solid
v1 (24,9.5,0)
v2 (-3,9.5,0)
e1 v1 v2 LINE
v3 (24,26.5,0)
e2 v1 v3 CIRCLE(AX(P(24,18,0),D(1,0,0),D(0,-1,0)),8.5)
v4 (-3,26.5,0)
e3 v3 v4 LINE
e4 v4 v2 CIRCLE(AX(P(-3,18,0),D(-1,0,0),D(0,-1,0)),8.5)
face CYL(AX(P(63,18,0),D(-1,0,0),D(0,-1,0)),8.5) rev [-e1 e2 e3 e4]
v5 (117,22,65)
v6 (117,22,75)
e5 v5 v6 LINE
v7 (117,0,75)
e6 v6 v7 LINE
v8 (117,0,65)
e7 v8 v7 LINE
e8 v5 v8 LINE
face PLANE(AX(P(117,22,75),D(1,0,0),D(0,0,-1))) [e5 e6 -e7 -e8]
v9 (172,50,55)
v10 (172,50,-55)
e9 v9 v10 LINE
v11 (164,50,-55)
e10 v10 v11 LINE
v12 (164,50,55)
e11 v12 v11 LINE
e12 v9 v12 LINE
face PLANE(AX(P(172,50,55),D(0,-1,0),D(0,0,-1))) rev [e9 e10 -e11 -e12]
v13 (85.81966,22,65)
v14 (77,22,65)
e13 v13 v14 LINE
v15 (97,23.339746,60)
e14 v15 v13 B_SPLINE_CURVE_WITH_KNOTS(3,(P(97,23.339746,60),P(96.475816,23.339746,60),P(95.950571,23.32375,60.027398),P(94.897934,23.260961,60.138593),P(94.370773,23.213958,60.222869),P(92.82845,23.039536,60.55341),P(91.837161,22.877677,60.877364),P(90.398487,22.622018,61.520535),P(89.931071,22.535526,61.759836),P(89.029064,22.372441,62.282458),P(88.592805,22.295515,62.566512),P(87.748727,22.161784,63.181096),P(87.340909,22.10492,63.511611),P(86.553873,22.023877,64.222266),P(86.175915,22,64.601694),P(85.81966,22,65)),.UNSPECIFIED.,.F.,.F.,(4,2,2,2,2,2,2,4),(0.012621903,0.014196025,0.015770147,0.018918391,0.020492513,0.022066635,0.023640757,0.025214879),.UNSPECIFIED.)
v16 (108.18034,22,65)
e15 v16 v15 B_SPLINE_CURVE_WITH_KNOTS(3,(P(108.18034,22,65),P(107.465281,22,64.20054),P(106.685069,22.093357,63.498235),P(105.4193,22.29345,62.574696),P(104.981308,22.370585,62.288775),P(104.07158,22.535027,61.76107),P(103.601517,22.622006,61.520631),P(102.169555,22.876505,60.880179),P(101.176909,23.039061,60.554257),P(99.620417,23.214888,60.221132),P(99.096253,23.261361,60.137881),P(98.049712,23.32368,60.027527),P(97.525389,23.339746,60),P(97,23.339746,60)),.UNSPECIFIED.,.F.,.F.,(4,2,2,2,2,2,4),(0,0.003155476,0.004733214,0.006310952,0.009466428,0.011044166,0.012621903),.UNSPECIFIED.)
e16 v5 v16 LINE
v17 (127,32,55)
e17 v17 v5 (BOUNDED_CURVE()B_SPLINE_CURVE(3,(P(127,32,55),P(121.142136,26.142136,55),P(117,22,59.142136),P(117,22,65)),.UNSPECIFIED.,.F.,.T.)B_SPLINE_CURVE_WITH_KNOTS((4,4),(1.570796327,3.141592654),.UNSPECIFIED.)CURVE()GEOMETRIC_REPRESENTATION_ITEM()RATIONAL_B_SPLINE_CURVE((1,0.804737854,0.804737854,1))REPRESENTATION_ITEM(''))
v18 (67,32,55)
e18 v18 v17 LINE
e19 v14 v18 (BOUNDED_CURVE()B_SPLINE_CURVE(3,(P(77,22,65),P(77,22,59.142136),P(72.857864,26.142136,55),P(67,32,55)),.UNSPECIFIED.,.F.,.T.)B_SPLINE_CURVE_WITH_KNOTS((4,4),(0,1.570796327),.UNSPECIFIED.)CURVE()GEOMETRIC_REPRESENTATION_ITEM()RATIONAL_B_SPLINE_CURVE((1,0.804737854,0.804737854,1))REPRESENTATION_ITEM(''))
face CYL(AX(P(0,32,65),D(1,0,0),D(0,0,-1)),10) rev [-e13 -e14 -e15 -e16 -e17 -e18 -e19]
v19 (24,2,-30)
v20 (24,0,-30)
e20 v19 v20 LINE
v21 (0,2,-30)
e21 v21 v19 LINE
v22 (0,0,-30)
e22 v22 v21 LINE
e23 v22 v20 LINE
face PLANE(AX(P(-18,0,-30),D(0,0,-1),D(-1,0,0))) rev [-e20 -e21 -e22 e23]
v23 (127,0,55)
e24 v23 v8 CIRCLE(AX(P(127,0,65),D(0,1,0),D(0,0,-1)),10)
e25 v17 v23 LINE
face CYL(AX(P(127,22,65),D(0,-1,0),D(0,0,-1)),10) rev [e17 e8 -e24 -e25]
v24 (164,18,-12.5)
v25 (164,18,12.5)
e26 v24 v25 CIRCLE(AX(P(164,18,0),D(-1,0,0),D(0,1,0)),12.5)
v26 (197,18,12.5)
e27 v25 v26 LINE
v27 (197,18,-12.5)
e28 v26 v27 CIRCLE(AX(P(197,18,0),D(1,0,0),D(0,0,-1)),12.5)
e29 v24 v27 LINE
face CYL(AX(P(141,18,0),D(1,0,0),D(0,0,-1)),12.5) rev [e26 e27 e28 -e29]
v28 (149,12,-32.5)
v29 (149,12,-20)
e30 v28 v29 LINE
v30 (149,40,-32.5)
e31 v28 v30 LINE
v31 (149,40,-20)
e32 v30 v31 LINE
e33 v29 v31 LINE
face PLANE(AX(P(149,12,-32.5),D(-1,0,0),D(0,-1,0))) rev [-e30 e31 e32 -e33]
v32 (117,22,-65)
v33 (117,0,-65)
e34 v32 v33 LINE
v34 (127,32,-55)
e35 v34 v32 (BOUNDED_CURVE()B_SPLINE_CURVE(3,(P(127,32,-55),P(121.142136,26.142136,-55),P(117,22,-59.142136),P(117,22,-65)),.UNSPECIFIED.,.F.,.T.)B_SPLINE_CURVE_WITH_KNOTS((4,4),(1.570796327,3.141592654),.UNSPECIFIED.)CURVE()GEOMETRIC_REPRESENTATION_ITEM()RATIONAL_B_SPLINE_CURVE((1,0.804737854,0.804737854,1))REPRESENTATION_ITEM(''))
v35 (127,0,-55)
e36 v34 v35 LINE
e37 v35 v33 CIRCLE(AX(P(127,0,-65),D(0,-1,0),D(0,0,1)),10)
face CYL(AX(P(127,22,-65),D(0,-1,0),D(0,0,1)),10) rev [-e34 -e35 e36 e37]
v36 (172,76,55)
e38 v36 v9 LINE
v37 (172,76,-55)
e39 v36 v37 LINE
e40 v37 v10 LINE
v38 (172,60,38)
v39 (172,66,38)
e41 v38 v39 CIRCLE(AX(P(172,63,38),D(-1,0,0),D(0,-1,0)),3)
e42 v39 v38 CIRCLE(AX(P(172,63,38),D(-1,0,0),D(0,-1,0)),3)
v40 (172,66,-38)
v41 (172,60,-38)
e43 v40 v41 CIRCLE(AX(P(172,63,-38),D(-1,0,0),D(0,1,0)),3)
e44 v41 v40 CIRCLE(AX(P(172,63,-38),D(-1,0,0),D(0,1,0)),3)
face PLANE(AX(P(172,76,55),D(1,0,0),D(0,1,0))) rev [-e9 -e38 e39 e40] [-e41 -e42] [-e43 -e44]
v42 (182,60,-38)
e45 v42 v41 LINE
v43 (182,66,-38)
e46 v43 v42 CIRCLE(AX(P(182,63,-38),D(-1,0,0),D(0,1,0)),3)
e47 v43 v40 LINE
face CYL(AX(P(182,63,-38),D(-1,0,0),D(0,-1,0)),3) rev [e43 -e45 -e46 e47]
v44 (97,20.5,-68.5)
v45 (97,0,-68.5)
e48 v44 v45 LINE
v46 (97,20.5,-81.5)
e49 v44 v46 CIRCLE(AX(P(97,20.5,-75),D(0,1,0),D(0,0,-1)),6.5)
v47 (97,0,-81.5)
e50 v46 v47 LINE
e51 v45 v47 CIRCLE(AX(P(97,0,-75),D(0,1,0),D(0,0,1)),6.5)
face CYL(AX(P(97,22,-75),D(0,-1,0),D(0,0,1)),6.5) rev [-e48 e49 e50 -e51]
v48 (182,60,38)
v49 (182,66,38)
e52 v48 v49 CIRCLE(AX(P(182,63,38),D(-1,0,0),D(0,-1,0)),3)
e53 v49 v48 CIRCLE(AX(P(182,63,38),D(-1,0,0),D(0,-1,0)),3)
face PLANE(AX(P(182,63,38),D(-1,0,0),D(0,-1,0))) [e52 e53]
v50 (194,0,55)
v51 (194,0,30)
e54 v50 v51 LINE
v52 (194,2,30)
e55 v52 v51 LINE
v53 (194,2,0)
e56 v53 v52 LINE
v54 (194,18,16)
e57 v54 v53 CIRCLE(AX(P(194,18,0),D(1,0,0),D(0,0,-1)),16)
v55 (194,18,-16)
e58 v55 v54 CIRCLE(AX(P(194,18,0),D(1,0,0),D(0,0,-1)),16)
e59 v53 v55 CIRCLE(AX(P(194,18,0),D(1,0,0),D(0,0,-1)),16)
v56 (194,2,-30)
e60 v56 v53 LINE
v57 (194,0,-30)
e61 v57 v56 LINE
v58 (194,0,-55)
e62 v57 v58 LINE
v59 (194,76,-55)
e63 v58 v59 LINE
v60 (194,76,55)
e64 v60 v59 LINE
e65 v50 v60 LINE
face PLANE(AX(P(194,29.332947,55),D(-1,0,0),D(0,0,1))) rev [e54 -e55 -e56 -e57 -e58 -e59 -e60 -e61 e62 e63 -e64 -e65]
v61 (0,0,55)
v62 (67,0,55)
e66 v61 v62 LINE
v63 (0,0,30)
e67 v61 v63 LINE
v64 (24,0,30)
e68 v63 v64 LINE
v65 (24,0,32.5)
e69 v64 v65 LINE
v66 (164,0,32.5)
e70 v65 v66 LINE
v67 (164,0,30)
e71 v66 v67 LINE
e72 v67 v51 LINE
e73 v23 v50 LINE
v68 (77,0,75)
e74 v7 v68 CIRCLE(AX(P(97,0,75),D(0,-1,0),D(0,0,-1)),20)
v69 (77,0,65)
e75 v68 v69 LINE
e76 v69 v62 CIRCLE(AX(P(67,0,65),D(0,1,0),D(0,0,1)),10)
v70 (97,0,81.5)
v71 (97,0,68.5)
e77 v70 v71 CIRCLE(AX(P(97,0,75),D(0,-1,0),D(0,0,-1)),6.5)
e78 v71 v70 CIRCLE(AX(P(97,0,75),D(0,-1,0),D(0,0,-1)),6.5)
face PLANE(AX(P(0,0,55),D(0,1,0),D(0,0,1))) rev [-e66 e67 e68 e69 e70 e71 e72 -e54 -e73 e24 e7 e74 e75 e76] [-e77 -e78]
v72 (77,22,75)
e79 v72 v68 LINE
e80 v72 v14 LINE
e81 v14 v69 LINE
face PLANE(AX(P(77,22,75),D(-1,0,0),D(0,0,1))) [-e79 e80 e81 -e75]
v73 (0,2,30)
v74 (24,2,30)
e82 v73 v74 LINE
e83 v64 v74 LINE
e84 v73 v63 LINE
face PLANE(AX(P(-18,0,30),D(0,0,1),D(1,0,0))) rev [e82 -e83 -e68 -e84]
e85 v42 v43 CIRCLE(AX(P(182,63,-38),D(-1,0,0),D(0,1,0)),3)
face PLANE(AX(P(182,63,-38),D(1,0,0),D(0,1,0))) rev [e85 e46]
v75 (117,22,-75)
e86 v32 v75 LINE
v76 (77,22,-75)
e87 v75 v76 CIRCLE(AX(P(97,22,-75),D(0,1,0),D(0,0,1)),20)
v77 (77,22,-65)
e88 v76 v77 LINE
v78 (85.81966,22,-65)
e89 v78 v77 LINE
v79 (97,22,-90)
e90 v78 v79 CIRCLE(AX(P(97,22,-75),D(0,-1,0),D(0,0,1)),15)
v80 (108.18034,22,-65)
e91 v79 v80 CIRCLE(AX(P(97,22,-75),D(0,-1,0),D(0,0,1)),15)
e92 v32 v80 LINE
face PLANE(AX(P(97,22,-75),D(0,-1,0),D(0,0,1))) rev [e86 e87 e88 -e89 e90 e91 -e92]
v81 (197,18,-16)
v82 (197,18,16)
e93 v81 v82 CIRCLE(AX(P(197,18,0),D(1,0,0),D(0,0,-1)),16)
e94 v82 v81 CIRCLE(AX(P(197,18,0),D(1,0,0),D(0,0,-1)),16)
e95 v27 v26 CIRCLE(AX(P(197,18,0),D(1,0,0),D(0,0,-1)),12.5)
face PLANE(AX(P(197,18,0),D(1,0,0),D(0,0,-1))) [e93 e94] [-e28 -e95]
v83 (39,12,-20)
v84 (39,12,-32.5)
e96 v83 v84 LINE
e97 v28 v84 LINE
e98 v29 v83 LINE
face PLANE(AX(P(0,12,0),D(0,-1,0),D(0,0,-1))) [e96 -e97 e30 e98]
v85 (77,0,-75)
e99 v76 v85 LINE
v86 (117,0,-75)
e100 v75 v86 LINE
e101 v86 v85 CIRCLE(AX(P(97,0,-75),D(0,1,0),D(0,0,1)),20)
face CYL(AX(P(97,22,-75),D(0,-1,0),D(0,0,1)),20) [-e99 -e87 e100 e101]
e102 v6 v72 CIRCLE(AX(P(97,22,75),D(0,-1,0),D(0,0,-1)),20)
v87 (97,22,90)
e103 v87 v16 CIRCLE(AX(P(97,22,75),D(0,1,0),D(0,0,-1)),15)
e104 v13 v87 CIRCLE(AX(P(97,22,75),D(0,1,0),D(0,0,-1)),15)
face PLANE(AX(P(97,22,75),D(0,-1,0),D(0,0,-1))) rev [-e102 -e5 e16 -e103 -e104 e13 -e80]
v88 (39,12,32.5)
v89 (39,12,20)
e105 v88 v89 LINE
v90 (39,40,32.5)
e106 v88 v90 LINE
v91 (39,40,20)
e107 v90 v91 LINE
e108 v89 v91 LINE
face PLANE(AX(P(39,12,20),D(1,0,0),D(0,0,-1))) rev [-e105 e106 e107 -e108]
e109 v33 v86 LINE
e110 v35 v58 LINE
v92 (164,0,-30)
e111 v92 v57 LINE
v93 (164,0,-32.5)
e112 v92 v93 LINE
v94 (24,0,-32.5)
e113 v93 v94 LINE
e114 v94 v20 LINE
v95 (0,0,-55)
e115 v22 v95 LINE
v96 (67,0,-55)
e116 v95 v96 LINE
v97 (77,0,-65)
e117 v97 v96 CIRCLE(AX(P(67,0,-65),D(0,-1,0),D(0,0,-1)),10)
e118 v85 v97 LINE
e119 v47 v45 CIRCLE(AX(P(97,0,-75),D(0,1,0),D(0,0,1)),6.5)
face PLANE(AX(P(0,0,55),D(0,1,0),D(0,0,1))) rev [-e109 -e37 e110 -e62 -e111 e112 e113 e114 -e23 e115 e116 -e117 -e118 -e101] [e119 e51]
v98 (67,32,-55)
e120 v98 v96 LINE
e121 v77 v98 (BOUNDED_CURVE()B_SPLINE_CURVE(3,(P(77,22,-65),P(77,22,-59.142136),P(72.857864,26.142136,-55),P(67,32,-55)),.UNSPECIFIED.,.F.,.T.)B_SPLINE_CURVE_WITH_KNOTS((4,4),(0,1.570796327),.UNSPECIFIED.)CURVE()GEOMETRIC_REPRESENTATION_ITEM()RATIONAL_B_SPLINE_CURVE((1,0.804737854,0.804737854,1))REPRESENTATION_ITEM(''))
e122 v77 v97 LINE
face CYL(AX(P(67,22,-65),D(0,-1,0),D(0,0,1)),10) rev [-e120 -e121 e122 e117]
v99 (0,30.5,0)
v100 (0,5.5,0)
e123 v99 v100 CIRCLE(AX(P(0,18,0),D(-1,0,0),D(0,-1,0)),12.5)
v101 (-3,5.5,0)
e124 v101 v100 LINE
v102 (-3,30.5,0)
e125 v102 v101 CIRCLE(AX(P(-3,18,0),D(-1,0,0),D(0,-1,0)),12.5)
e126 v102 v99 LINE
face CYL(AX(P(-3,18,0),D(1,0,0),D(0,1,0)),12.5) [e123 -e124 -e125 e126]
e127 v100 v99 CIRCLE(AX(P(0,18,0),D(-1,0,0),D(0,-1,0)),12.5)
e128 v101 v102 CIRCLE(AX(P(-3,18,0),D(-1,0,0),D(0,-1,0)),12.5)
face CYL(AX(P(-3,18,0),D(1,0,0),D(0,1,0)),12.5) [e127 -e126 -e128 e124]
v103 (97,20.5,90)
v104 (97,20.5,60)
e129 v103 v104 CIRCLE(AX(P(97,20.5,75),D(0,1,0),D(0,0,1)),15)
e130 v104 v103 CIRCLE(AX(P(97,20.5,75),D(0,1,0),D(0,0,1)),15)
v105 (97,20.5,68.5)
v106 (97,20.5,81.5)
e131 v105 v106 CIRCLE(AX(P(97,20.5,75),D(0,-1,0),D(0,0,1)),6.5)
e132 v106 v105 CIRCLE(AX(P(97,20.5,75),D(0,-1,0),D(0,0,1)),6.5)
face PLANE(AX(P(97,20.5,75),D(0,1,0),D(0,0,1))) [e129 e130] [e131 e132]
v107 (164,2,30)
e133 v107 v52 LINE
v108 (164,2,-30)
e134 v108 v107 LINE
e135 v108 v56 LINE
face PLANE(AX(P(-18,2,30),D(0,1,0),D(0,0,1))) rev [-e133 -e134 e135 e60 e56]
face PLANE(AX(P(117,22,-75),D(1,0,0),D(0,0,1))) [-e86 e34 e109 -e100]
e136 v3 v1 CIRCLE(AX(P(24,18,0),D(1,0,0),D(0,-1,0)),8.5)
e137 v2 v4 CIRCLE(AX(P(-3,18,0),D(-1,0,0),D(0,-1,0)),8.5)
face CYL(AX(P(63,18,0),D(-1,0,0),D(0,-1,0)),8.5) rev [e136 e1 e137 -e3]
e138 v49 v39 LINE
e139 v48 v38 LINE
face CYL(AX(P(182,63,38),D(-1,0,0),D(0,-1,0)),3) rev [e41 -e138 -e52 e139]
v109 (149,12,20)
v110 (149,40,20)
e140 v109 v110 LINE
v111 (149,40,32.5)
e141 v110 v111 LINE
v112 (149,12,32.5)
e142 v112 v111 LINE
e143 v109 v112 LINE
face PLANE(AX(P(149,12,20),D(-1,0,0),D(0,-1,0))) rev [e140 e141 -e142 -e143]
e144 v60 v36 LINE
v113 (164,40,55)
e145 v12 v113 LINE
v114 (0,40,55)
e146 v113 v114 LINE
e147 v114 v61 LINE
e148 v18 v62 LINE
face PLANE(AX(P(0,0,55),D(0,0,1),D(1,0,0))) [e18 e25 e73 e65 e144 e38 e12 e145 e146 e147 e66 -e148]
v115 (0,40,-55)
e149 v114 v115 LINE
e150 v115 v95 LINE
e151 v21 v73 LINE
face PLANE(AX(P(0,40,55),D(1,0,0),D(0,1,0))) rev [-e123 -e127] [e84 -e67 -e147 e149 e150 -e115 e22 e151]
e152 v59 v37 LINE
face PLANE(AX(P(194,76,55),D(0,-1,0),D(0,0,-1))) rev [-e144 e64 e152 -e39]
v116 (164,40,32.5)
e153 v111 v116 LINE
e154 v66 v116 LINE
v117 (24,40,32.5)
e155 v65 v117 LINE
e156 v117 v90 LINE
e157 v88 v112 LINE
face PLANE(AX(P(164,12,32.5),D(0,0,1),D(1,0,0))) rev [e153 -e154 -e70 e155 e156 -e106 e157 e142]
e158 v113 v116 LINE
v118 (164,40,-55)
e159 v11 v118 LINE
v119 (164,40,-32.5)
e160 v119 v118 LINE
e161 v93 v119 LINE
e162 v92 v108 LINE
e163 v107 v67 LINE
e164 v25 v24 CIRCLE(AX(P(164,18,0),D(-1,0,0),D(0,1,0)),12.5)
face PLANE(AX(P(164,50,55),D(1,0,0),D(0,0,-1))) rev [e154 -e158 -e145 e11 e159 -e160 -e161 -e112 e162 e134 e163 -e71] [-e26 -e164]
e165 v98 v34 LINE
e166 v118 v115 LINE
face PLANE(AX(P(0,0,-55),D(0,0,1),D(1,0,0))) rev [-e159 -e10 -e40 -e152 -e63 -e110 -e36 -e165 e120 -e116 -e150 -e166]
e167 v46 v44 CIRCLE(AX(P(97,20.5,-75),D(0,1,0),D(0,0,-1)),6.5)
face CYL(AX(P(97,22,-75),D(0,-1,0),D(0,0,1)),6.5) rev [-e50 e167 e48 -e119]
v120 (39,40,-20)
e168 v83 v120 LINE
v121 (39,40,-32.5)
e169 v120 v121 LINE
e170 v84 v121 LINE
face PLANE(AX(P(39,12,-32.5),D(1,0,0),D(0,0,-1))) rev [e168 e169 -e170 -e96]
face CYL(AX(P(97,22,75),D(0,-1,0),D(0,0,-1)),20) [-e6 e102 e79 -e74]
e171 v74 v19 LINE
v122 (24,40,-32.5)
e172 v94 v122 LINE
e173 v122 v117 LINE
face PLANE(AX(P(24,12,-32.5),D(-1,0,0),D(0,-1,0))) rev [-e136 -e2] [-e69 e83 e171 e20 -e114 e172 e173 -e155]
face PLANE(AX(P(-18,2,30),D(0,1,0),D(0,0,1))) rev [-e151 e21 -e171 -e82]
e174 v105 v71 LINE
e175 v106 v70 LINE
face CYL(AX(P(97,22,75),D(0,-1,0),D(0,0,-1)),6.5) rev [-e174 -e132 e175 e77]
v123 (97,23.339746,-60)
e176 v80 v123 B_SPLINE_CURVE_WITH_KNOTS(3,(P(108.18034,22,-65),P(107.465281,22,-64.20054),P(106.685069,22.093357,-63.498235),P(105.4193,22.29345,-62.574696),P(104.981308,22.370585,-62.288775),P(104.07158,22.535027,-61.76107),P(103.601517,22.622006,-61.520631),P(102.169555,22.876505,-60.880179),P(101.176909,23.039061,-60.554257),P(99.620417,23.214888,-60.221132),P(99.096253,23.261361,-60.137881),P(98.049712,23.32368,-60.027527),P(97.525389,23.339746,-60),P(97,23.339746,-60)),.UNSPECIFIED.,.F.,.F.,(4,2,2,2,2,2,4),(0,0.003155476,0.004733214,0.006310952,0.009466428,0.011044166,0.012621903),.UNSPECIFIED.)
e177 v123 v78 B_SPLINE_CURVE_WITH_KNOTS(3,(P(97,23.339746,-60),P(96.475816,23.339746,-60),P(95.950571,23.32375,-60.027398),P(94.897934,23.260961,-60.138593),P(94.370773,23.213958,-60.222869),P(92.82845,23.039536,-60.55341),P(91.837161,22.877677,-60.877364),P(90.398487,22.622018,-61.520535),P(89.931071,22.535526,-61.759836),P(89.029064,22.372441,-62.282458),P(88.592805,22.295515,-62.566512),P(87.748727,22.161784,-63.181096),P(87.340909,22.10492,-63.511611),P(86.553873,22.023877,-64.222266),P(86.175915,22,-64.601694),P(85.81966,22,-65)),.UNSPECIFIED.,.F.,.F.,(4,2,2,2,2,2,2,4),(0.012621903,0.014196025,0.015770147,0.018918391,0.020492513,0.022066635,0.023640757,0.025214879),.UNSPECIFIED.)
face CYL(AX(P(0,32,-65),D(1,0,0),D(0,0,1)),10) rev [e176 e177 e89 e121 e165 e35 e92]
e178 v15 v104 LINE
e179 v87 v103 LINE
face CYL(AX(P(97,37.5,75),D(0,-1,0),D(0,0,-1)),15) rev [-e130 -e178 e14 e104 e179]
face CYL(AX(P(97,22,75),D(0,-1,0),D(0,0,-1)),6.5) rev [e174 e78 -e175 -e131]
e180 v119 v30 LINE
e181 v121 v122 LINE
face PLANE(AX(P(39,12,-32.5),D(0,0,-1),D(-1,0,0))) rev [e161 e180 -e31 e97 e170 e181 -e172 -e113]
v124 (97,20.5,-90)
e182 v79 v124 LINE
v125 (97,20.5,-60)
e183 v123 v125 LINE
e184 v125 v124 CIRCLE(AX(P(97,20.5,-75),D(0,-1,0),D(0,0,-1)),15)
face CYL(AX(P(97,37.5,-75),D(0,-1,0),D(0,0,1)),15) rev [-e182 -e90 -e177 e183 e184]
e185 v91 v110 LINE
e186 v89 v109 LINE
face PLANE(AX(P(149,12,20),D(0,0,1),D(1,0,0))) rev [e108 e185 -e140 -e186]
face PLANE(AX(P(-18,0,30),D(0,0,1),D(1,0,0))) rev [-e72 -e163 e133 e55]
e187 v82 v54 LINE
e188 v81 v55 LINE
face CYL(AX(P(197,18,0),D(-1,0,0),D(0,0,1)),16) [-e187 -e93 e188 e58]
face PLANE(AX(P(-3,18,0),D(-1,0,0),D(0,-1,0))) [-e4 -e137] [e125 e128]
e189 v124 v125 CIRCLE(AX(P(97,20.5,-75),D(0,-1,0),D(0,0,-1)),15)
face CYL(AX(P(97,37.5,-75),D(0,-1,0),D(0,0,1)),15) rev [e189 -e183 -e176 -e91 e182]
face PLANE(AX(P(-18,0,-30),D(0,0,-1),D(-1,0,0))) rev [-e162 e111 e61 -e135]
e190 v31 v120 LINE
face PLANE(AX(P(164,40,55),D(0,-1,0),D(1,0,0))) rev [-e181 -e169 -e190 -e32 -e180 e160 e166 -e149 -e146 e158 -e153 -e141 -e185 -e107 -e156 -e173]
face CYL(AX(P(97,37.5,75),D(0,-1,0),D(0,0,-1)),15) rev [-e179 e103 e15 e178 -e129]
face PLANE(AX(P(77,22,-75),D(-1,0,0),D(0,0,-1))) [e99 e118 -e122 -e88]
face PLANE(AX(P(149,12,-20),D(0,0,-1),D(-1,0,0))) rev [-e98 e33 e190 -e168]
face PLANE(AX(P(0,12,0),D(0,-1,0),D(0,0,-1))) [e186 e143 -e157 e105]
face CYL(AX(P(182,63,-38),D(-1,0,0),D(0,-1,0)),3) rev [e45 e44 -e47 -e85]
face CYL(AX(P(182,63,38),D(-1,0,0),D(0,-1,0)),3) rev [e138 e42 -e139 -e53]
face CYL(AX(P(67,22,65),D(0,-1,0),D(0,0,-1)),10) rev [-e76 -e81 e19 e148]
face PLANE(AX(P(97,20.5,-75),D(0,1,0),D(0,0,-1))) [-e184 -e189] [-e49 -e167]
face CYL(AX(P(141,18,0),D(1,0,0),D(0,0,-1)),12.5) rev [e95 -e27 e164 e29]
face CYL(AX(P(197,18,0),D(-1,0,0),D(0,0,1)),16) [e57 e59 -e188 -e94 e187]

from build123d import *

# Parameters (mm, degrees)
BOSS_EXTRUDE1_DEPTH     = 55
SKETCH2_W               = 60
SKETCH2_H               = 2
CUT_EXTRUDE1_DEPTH      = 212
SKETCH3_R               = 16
BOSS_EXTRUDE2_DEPTH     = 3
SKETCH4_R               = 12.5
CUT_EXTRUDE2_DEPTH      = 56
SKETCH5_R               = 12.5
BOSS_EXTRUDE3_DEPTH     = 3
SKETCH6_R               = 8.5
CUT_EXTRUDE3_DEPTH      = 66
CUT_EXTRUDE4_DEPTH      = 28
SKETCH9_R               = 6.5
BOSS_EXTRUDE4_DEPTH     = 22
FILLET1_R               = 10
CUT_EXTRUDE5_DEPTH      = 15.5
CUT_EXTRUDE5_DEPTH_BACK = 1.5
SKETCH10_R              = 15
SKETCH12_W              = 110
SKETCH12_H              = 12.5
SKETCH12_H_2            = 2.5
SKETCH12_H_3            = 10
SKETCH12_W_2            = 15
CUT_EXTRUDE7_DEPTH      = 12
SKETCH13_R              = 3
CUT_EXTRUDE8_DEPTH      = 10


with BuildPart() as part:
    # Sketch1 → Boss-Extrude1 (new, symmetric)
    with BuildSketch(Plane.XY):
        Polygon((0, 0), (194, 0), (194, 29.332947361), (194, 76), (172, 76), (172, 50), (164, 50), (164, 40), (0, 40), align=None)
    extrude(amount=BOSS_EXTRUDE1_DEPTH, both=True)

    # Sketch2 → Cut-Extrude1 (cut)
    with BuildSketch(Plane(origin=(194, 0, 0), x_dir=(0, 0, -1), z_dir=(1, 0, 0))):
        with Locations((0, 1)):
            Rectangle(SKETCH2_W, SKETCH2_H)
    extrude(amount=-CUT_EXTRUDE1_DEPTH, mode=Mode.SUBTRACT)

    # Sketch3 → Boss-Extrude2 (add)
    with BuildSketch(Plane(origin=(194, 0, 0), x_dir=(0, 0, -1), z_dir=(1, 0, 0))):
        with Locations(Location((0, 18, 0), (0, 0, 270))):
            Circle(SKETCH3_R)
    extrude(amount=BOSS_EXTRUDE2_DEPTH)

    # Sketch4 → Cut-Extrude2 (cut)
    with BuildSketch(Plane(origin=(197, 0, 0), x_dir=(0, 0, -1), z_dir=(1, 0, 0))):
        with Locations((0, 18)):
            Circle(SKETCH4_R)
    extrude(amount=-CUT_EXTRUDE2_DEPTH, mode=Mode.SUBTRACT)

    # Sketch5 → Boss-Extrude3 (add)
    with BuildSketch(Plane.ZY):
        with Locations(Location((0, 18, 0), (0, 0, 180))):
            Circle(SKETCH5_R)
    extrude(amount=BOSS_EXTRUDE3_DEPTH)

    # Sketch6 → Cut-Extrude3 (cut)
    with BuildSketch(Plane.ZY.offset(3)):
        with Locations(Location((0, 18, 0), (0, 0, 270))):
            Circle(SKETCH6_R)
    extrude(amount=-CUT_EXTRUDE3_DEPTH, mode=Mode.SUBTRACT)

    # Sketch7 → Cut-Extrude4 (cut)
    with BuildSketch(Plane(origin=(0, 40, 0), x_dir=(1, 0, 0), z_dir=(0, 1, 0))):
        Polygon((164, 32.5), (149, 32.5), (149, 20), (39, 20), (39, 32.5), (24, 32.5), (24, -32.5), (39, -32.5), (39, -20), (149, -20), (149, -32.5), (164, -32.5), align=None)
    extrude(amount=-CUT_EXTRUDE4_DEPTH, mode=Mode.SUBTRACT)

    # Sketch9 → Boss-Extrude4 (add)
    with BuildSketch(Plane.XZ):
        with BuildLine():
            Line((117, 75), (117, 65))
            ThreePointArc((117, 65), (119.928932188, 57.928932188), (127, 55))
            Line((127, 55), (67, 55))
            ThreePointArc((67, 55), (74.071067812, 57.928932188), (77, 65))
            Line((77, 65), (77, 75))
            ThreePointArc((77, 75), (97, 95), (117, 75))
        make_face()
        with Locations(Location((97, 75, 0), (0, 0, 270))):
            Circle(SKETCH9_R, mode=Mode.SUBTRACT)
    extrude(amount=-BOSS_EXTRUDE4_DEPTH)

    # Fillet1
    fillet1_edges = [part.edges().sort_by_distance(p)[0] for p in [
        (97, 22, 55),
    ]]
    fillet(fillet1_edges, radius=FILLET1_R)

    # Sketch10 → Cut-Extrude5 (cut, two sides: drawn at the far end of the back side and taken through both)
    with BuildSketch(Plane(origin=(0, 22, 0), x_dir=(1, 0, 0), z_dir=(0, 1, 0)).offset(-CUT_EXTRUDE5_DEPTH_BACK)):
        with Locations(Location((97, -75, 0), (0, 0, 138.189685104))):
            Circle(SKETCH10_R)
    extrude(amount=CUT_EXTRUDE5_DEPTH + CUT_EXTRUDE5_DEPTH_BACK, mode=Mode.SUBTRACT)

    # Mirror17: part across plane


with BuildPart() as part_1:
    add(part.part)
    add(part.part.mirror(Plane.XY))

    # Sketch12 → Cut-Extrude7 (cut)
    with BuildSketch(Plane.XZ):
        Polygon((149, 20), (39, 20), (39, 32.5), (24, 32.5), (24, -30), (39, -30), (39, -20), (149, -20), (149, -30), (164, -30), (164, 32.5), (149, 32.5), align=None)
        with Locations((94, 26.25)):
            Rectangle(SKETCH12_W, SKETCH12_H)
        with Locations((94, -31.25)):
            Rectangle(SKETCH12_W, SKETCH12_H_2)
        with Locations((94, -25)):
            Rectangle(SKETCH12_W, SKETCH12_H_3)
        with Locations((31.5, -31.25)):
            Rectangle(SKETCH12_W_2, SKETCH12_H_2)
        with Locations((156.5, -31.25)):
            Rectangle(SKETCH12_W_2, SKETCH12_H_2)
    extrude(amount=-CUT_EXTRUDE7_DEPTH, mode=Mode.SUBTRACT)

    # Sketch13 → Cut-Extrude8 (cut)
    with BuildSketch(Plane.ZY.offset(-172)):
        with Locations(Location((38, 63, 0), (0, 0, 270))):
            Circle(SKETCH13_R)
        with Locations(Location((-38, 63, 0), (0, 0, 90))):
            Circle(SKETCH13_R)
    extrude(amount=-CUT_EXTRUDE8_DEPTH, mode=Mode.SUBTRACT)


solid = part_1.part
